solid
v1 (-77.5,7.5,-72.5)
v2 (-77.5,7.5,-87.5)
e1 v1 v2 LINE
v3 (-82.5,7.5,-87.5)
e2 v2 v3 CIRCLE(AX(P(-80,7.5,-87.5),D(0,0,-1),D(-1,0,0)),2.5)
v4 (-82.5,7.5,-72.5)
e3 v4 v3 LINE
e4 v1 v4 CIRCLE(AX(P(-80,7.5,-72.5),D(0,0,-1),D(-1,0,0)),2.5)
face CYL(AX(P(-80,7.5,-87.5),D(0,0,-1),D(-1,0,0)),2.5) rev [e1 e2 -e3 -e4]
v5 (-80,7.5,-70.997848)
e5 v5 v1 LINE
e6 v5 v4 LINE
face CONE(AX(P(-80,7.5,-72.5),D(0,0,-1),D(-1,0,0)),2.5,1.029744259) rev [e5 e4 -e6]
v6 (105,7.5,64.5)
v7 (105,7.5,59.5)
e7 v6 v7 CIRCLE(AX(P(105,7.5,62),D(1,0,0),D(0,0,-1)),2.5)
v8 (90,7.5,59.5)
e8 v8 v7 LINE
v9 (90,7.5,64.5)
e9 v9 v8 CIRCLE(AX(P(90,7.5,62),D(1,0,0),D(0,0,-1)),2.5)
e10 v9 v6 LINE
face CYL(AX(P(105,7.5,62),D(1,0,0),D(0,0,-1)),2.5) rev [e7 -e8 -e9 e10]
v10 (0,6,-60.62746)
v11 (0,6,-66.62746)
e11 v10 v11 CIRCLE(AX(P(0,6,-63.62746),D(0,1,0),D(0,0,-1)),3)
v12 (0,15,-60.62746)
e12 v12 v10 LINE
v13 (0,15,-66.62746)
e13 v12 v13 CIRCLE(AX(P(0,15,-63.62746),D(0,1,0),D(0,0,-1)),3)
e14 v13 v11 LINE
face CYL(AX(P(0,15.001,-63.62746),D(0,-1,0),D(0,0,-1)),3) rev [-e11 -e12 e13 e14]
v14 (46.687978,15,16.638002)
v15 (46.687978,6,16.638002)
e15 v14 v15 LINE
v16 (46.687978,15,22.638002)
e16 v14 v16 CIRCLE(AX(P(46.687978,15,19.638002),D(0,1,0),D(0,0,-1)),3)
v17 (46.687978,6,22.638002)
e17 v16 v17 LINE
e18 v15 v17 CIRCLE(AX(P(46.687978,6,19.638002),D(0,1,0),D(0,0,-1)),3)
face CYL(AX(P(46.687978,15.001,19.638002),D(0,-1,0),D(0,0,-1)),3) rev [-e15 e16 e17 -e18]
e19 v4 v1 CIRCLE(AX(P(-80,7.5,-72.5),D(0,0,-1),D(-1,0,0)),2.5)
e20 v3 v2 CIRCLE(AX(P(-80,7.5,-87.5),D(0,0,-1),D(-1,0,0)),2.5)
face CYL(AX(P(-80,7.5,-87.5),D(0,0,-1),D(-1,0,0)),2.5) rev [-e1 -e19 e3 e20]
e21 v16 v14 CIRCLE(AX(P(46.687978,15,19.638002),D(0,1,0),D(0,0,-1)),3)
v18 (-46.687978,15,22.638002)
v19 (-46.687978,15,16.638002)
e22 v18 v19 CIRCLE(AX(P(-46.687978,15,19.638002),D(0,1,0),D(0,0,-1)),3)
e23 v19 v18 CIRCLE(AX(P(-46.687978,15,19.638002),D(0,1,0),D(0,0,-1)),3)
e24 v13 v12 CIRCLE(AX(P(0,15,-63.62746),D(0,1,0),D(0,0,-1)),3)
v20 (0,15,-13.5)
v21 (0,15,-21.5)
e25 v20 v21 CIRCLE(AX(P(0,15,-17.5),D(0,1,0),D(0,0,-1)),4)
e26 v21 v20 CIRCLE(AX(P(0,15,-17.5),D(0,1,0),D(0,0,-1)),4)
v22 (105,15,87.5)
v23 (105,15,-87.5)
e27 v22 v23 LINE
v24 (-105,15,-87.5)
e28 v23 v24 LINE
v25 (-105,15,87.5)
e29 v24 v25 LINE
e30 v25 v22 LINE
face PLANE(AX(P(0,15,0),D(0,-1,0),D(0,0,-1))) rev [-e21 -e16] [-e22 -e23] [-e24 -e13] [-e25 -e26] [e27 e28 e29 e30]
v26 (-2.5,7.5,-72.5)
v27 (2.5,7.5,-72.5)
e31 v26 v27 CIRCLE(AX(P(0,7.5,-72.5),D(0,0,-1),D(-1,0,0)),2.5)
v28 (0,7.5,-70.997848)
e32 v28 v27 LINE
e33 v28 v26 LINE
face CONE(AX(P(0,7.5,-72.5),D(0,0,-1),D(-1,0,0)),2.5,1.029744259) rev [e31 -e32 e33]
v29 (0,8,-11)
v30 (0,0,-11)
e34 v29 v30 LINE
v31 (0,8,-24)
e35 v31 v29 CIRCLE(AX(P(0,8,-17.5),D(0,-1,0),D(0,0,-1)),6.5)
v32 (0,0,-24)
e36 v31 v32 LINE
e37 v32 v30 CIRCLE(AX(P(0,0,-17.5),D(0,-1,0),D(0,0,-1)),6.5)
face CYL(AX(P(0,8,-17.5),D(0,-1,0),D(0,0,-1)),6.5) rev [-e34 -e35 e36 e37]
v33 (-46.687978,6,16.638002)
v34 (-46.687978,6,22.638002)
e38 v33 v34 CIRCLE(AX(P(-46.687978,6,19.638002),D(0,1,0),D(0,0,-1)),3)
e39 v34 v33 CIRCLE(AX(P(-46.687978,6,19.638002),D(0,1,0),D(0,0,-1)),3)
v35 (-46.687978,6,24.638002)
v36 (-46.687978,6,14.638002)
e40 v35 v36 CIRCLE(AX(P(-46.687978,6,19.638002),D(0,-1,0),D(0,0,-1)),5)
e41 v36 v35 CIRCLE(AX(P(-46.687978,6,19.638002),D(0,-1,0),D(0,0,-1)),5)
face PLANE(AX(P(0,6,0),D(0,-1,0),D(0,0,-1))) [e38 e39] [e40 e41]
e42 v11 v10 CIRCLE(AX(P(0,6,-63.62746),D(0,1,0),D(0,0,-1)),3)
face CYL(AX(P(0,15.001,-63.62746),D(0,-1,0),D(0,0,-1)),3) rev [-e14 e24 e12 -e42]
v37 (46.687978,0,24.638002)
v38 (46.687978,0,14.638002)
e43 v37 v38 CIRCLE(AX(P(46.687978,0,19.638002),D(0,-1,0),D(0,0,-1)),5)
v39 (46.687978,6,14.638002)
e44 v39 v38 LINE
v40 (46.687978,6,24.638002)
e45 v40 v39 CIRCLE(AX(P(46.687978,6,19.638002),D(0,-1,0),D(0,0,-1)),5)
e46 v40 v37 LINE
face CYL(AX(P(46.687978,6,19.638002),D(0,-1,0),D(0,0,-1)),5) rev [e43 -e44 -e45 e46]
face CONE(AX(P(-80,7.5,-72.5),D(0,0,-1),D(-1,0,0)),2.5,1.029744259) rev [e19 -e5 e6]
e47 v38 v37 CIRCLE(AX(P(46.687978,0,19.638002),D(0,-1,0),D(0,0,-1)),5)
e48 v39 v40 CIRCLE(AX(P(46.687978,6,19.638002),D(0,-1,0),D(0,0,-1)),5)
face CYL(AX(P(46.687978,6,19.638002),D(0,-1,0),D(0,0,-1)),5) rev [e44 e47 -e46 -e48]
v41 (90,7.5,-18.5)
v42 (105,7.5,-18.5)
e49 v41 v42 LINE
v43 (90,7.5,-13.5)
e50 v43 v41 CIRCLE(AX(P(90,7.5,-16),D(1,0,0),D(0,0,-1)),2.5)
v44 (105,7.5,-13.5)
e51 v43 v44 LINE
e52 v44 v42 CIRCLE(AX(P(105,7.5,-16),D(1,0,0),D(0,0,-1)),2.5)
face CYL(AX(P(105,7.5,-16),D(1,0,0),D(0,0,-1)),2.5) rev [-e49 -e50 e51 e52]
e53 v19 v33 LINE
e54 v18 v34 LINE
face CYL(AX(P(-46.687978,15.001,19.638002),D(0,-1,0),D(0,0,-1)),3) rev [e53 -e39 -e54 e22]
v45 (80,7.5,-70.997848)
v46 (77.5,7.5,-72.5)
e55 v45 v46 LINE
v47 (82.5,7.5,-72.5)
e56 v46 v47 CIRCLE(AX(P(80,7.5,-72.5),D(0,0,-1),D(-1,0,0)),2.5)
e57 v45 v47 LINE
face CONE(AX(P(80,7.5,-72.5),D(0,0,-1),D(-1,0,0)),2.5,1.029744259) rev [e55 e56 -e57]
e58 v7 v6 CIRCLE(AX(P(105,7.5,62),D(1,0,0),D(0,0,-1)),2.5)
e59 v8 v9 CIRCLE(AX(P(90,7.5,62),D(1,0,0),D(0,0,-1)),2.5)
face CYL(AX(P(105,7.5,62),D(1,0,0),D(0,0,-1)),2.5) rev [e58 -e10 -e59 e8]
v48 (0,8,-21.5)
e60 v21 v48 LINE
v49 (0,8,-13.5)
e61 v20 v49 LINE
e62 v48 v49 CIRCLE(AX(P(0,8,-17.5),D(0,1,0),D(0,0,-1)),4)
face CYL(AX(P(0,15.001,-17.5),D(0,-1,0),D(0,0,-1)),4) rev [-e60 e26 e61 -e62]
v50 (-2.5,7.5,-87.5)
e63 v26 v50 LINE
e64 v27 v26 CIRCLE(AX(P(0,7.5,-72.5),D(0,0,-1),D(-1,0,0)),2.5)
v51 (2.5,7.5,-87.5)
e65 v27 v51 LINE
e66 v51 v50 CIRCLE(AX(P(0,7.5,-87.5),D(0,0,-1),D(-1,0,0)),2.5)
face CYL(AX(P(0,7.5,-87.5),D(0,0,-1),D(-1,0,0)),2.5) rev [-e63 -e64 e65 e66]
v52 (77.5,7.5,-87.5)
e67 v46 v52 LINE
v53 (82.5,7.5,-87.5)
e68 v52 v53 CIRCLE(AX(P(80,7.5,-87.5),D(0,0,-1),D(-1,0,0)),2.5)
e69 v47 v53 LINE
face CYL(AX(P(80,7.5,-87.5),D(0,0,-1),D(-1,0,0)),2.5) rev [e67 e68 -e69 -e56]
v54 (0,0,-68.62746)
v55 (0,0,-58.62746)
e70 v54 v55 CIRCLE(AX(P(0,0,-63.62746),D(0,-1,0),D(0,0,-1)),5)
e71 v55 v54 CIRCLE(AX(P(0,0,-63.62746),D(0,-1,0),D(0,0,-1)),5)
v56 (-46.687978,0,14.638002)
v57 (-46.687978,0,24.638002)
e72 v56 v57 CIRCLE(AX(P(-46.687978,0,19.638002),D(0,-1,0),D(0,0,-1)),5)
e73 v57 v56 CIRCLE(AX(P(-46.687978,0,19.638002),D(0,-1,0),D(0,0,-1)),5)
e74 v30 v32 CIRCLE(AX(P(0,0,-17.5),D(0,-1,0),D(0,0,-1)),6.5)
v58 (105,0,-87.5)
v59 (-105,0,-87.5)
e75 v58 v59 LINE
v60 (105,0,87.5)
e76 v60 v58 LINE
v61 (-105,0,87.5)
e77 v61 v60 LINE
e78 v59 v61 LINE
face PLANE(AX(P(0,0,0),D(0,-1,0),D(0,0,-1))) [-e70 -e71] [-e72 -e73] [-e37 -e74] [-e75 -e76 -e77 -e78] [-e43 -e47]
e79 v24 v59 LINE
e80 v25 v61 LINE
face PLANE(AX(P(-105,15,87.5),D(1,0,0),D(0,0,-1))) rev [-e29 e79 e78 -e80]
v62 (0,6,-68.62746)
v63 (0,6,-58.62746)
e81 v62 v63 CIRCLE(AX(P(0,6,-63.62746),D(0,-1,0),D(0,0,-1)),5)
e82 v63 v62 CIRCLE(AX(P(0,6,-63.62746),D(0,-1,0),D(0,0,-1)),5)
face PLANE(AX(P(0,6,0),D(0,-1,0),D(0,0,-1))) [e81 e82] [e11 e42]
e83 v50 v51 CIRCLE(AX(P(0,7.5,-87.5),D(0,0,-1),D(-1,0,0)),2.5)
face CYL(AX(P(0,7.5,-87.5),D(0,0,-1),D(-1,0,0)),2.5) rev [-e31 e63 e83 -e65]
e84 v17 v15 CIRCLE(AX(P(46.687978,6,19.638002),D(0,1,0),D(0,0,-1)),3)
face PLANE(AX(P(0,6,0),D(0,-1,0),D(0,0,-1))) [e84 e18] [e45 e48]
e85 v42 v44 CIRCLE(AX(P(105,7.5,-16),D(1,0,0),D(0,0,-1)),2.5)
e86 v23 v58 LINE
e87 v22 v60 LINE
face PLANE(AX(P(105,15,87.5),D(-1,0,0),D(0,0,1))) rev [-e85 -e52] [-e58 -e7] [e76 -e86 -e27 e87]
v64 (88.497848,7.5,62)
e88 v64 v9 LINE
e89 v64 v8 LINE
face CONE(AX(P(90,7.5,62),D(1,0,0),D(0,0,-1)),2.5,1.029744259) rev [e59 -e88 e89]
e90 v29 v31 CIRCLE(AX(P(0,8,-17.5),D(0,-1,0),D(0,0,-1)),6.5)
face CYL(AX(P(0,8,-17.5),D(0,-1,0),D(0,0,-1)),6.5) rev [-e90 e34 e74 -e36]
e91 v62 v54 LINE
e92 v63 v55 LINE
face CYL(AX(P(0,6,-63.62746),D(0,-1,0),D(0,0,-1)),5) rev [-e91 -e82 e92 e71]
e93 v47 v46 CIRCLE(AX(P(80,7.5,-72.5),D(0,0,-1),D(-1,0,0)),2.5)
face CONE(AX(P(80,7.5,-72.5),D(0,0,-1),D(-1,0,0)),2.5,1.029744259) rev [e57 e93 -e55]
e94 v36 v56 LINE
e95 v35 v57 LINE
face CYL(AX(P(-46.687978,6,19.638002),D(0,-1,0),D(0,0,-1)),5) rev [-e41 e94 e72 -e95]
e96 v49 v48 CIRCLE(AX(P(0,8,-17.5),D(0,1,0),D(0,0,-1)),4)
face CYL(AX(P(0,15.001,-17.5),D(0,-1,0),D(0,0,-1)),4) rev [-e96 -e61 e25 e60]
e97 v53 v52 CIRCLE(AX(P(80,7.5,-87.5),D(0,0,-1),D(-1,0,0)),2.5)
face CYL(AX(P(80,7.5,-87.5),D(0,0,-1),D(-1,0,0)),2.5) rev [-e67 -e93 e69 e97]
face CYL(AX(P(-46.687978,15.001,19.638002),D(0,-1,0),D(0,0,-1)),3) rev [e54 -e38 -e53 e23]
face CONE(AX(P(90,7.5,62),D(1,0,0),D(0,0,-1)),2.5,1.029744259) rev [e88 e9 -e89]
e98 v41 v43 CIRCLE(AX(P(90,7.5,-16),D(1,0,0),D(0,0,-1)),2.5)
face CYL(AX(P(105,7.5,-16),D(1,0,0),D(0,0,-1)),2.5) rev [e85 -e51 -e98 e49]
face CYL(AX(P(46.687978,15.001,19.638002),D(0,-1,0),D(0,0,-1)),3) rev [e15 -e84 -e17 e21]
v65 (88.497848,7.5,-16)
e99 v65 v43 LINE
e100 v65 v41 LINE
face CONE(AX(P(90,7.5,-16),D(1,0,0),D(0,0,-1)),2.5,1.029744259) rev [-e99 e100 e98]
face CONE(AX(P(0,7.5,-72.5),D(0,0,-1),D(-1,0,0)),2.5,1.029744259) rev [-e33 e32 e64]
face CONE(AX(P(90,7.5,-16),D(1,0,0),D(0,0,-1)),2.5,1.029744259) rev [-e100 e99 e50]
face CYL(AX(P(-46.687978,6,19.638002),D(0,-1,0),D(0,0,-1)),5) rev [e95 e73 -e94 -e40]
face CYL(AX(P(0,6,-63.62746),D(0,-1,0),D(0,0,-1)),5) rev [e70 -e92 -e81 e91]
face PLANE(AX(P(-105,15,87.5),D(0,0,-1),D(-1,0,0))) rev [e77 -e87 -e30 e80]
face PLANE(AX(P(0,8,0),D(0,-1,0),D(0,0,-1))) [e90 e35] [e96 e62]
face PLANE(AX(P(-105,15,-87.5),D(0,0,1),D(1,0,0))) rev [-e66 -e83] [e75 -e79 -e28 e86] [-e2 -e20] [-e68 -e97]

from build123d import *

# Parameters (mm, degrees)
SKETCH1_W                 = 210
SKETCH1_H                 = 175
BOSS_EXTRUDE1_DEPTH       = 15
SKETCH3_R                 = 5
SKETCH3_R_2               = 3
CUT_EXTRUDE1_DEPTH        = 6
CUT_EXTRUDE2_REACH        = 139.5
SKETCH3_3_R               = 3
M6X1_0_TAPPED_HOLE1_D     = 5
M6X1_0_TAPPED_HOLE1_DEPTH = 15
M6X1_0_TAPPED_HOLE1_TIP   = 1.502151548
M6X1_0_TAPPED_HOLE2_D     = 5
M6X1_0_TAPPED_HOLE2_DEPTH = 15
M6X1_0_TAPPED_HOLE2_TIP   = 1.502151548
SKETCH8_R                 = 6.5
SKETCH8_R_2               = 4
CUT_EXTRUDE3_DEPTH        = 8
CUT_EXTRUDE4_REACH        = 139.5
SKETCH8_3_R               = 4


with BuildPart() as part:
    # Sketch1 → Boss-Extrude1 (new body)
    with BuildSketch(Plane(origin=(0, 0, 0), x_dir=(1, 0, 0), z_dir=(0, 1, 0))):
        Rectangle(SKETCH1_W, SKETCH1_H)
    extrude(amount=BOSS_EXTRUDE1_DEPTH)

    # Sketch3 → Cut-Extrude1 (cut)
    # profile 1 of 3: a face of its own
    with BuildSketch(Plane.XZ):
        with Locations(Location((-46.687978245, 19.63800195, 0), (0, 0, 270))):
            Circle(SKETCH3_R)
        with Locations(Location((-46.687978245, 19.63800195, 0), (0, 0, 270))):
            Circle(SKETCH3_R_2, mode=Mode.SUBTRACT)
    # profile 2 of 3: a face of its own
    with BuildSketch(Plane.XZ):
        with Locations(Location((46.687978245, 19.63800195, 0), (0, 0, 270))):
            Circle(SKETCH3_R)
        with Locations(Location((46.687978245, 19.63800195, 0), (0, 0, 270))):
            Circle(SKETCH3_R_2, mode=Mode.SUBTRACT)
    # profile 3 of 3: a face of its own
    with BuildSketch(Plane.XZ):
        with Locations(Location((0, -63.6274596, 0), (0, 0, 270))):
            Circle(SKETCH3_R)
        with Locations(Location((0, -63.6274596, 0), (0, 0, 270))):
            Circle(SKETCH3_R_2, mode=Mode.SUBTRACT)
    extrude(amount=-CUT_EXTRUDE1_DEPTH, mode=Mode.SUBTRACT)

    # Sketch3<3> → Cut-Extrude2 (cut, up to next)
    with BuildSketch(Plane.XZ, mode=Mode.PRIVATE) as cut_extrude2_sk1:
        with Locations(Location((-46.687978245, 19.63800195, 0), (0, 0, 270))):
            Circle(SKETCH3_3_R)
    cut_extrude2_tool1 = extrude(cut_extrude2_sk1.sketch, amount=-CUT_EXTRUDE2_REACH, mode=Mode.PRIVATE) & part.part
    # Sketch3<3> → Cut-Extrude2 (cut, up to next)
    with BuildSketch(Plane.XZ, mode=Mode.PRIVATE) as cut_extrude2_sk2:
        with Locations(Location((46.687978245, 19.63800195, 0), (0, 0, 270))):
            Circle(SKETCH3_3_R)
    cut_extrude2_tool2 = extrude(cut_extrude2_sk2.sketch, amount=-CUT_EXTRUDE2_REACH, mode=Mode.PRIVATE) & part.part
    # Sketch3<3> → Cut-Extrude2 (cut, up to next)
    with BuildSketch(Plane.XZ, mode=Mode.PRIVATE) as cut_extrude2_sk3:
        with Locations(Location((0, -63.6274596, 0), (0, 0, 270))):
            Circle(SKETCH3_3_R)
    cut_extrude2_tool3 = extrude(cut_extrude2_sk3.sketch, amount=-CUT_EXTRUDE2_REACH, mode=Mode.PRIVATE) & part.part
    add(cut_extrude2_tool1.solids().sort_by_distance((-46.687978, 0, 19.638002))[0], mode=Mode.SUBTRACT)
    add(cut_extrude2_tool2.solids().sort_by_distance((46.687978, 0, 19.638002))[0], mode=Mode.SUBTRACT)
    add(cut_extrude2_tool3.solids().sort_by_distance((0, 0, -63.62746))[0], mode=Mode.SUBTRACT)

    # M6x1.0 Tapped Hole1
    with Locations(Plane(origin=(105, 7.5, -16), x_dir=(0, 0, 1), z_dir=(1, 0, 0))):
        with Locations((0, 0), (78, 0)):
            Hole(M6X1_0_TAPPED_HOLE1_D / 2, depth=M6X1_0_TAPPED_HOLE1_DEPTH)
            with Locations((0, 0, -(M6X1_0_TAPPED_HOLE1_DEPTH + M6X1_0_TAPPED_HOLE1_TIP / 2))):  # 118° drill point
                Cone(0, M6X1_0_TAPPED_HOLE1_D / 2, M6X1_0_TAPPED_HOLE1_TIP, mode=Mode.SUBTRACT)

    # M6x1.0 Tapped Hole2
    with Locations(Plane(origin=(80, 7.5, -87.5), x_dir=(-1, 0, 0), z_dir=(0, 0, -1))):
        with Locations((0, 0), (80, 0), (160, 0)):
            Hole(M6X1_0_TAPPED_HOLE2_D / 2, depth=M6X1_0_TAPPED_HOLE2_DEPTH)
            with Locations((0, 0, -(M6X1_0_TAPPED_HOLE2_DEPTH + M6X1_0_TAPPED_HOLE2_TIP / 2))):  # 118° drill point
                Cone(0, M6X1_0_TAPPED_HOLE2_D / 2, M6X1_0_TAPPED_HOLE2_TIP, mode=Mode.SUBTRACT)

    # Sketch8 → Cut-Extrude3 (cut)
    with BuildSketch(Plane(origin=(0, 0, 0), x_dir=(-1, 0, 0), z_dir=(0, -1, 0))):
        with Locations(Location((0, 17.5, 0), (0, 0, 90))):
            Circle(SKETCH8_R)
        with Locations(Location((0, 17.5, 0), (0, 0, 90))):
            Circle(SKETCH8_R_2, mode=Mode.SUBTRACT)
    extrude(amount=-CUT_EXTRUDE3_DEPTH, mode=Mode.SUBTRACT)

    # Sketch8<3> → Cut-Extrude4 (cut, up to next)
    with BuildSketch(Plane(origin=(0, 0, 0), x_dir=(-1, 0, 0), z_dir=(0, -1, 0)), mode=Mode.PRIVATE) as cut_extrude4_sk1:
        with Locations(Location((0, 17.5, 0), (0, 0, 90))):
            Circle(SKETCH8_3_R)
    cut_extrude4_tool1 = extrude(cut_extrude4_sk1.sketch, amount=-CUT_EXTRUDE4_REACH, mode=Mode.PRIVATE) & part.part
    add(cut_extrude4_tool1.solids().sort_by_distance((0, 0, -17.5))[0], mode=Mode.SUBTRACT)


solid = part.part
